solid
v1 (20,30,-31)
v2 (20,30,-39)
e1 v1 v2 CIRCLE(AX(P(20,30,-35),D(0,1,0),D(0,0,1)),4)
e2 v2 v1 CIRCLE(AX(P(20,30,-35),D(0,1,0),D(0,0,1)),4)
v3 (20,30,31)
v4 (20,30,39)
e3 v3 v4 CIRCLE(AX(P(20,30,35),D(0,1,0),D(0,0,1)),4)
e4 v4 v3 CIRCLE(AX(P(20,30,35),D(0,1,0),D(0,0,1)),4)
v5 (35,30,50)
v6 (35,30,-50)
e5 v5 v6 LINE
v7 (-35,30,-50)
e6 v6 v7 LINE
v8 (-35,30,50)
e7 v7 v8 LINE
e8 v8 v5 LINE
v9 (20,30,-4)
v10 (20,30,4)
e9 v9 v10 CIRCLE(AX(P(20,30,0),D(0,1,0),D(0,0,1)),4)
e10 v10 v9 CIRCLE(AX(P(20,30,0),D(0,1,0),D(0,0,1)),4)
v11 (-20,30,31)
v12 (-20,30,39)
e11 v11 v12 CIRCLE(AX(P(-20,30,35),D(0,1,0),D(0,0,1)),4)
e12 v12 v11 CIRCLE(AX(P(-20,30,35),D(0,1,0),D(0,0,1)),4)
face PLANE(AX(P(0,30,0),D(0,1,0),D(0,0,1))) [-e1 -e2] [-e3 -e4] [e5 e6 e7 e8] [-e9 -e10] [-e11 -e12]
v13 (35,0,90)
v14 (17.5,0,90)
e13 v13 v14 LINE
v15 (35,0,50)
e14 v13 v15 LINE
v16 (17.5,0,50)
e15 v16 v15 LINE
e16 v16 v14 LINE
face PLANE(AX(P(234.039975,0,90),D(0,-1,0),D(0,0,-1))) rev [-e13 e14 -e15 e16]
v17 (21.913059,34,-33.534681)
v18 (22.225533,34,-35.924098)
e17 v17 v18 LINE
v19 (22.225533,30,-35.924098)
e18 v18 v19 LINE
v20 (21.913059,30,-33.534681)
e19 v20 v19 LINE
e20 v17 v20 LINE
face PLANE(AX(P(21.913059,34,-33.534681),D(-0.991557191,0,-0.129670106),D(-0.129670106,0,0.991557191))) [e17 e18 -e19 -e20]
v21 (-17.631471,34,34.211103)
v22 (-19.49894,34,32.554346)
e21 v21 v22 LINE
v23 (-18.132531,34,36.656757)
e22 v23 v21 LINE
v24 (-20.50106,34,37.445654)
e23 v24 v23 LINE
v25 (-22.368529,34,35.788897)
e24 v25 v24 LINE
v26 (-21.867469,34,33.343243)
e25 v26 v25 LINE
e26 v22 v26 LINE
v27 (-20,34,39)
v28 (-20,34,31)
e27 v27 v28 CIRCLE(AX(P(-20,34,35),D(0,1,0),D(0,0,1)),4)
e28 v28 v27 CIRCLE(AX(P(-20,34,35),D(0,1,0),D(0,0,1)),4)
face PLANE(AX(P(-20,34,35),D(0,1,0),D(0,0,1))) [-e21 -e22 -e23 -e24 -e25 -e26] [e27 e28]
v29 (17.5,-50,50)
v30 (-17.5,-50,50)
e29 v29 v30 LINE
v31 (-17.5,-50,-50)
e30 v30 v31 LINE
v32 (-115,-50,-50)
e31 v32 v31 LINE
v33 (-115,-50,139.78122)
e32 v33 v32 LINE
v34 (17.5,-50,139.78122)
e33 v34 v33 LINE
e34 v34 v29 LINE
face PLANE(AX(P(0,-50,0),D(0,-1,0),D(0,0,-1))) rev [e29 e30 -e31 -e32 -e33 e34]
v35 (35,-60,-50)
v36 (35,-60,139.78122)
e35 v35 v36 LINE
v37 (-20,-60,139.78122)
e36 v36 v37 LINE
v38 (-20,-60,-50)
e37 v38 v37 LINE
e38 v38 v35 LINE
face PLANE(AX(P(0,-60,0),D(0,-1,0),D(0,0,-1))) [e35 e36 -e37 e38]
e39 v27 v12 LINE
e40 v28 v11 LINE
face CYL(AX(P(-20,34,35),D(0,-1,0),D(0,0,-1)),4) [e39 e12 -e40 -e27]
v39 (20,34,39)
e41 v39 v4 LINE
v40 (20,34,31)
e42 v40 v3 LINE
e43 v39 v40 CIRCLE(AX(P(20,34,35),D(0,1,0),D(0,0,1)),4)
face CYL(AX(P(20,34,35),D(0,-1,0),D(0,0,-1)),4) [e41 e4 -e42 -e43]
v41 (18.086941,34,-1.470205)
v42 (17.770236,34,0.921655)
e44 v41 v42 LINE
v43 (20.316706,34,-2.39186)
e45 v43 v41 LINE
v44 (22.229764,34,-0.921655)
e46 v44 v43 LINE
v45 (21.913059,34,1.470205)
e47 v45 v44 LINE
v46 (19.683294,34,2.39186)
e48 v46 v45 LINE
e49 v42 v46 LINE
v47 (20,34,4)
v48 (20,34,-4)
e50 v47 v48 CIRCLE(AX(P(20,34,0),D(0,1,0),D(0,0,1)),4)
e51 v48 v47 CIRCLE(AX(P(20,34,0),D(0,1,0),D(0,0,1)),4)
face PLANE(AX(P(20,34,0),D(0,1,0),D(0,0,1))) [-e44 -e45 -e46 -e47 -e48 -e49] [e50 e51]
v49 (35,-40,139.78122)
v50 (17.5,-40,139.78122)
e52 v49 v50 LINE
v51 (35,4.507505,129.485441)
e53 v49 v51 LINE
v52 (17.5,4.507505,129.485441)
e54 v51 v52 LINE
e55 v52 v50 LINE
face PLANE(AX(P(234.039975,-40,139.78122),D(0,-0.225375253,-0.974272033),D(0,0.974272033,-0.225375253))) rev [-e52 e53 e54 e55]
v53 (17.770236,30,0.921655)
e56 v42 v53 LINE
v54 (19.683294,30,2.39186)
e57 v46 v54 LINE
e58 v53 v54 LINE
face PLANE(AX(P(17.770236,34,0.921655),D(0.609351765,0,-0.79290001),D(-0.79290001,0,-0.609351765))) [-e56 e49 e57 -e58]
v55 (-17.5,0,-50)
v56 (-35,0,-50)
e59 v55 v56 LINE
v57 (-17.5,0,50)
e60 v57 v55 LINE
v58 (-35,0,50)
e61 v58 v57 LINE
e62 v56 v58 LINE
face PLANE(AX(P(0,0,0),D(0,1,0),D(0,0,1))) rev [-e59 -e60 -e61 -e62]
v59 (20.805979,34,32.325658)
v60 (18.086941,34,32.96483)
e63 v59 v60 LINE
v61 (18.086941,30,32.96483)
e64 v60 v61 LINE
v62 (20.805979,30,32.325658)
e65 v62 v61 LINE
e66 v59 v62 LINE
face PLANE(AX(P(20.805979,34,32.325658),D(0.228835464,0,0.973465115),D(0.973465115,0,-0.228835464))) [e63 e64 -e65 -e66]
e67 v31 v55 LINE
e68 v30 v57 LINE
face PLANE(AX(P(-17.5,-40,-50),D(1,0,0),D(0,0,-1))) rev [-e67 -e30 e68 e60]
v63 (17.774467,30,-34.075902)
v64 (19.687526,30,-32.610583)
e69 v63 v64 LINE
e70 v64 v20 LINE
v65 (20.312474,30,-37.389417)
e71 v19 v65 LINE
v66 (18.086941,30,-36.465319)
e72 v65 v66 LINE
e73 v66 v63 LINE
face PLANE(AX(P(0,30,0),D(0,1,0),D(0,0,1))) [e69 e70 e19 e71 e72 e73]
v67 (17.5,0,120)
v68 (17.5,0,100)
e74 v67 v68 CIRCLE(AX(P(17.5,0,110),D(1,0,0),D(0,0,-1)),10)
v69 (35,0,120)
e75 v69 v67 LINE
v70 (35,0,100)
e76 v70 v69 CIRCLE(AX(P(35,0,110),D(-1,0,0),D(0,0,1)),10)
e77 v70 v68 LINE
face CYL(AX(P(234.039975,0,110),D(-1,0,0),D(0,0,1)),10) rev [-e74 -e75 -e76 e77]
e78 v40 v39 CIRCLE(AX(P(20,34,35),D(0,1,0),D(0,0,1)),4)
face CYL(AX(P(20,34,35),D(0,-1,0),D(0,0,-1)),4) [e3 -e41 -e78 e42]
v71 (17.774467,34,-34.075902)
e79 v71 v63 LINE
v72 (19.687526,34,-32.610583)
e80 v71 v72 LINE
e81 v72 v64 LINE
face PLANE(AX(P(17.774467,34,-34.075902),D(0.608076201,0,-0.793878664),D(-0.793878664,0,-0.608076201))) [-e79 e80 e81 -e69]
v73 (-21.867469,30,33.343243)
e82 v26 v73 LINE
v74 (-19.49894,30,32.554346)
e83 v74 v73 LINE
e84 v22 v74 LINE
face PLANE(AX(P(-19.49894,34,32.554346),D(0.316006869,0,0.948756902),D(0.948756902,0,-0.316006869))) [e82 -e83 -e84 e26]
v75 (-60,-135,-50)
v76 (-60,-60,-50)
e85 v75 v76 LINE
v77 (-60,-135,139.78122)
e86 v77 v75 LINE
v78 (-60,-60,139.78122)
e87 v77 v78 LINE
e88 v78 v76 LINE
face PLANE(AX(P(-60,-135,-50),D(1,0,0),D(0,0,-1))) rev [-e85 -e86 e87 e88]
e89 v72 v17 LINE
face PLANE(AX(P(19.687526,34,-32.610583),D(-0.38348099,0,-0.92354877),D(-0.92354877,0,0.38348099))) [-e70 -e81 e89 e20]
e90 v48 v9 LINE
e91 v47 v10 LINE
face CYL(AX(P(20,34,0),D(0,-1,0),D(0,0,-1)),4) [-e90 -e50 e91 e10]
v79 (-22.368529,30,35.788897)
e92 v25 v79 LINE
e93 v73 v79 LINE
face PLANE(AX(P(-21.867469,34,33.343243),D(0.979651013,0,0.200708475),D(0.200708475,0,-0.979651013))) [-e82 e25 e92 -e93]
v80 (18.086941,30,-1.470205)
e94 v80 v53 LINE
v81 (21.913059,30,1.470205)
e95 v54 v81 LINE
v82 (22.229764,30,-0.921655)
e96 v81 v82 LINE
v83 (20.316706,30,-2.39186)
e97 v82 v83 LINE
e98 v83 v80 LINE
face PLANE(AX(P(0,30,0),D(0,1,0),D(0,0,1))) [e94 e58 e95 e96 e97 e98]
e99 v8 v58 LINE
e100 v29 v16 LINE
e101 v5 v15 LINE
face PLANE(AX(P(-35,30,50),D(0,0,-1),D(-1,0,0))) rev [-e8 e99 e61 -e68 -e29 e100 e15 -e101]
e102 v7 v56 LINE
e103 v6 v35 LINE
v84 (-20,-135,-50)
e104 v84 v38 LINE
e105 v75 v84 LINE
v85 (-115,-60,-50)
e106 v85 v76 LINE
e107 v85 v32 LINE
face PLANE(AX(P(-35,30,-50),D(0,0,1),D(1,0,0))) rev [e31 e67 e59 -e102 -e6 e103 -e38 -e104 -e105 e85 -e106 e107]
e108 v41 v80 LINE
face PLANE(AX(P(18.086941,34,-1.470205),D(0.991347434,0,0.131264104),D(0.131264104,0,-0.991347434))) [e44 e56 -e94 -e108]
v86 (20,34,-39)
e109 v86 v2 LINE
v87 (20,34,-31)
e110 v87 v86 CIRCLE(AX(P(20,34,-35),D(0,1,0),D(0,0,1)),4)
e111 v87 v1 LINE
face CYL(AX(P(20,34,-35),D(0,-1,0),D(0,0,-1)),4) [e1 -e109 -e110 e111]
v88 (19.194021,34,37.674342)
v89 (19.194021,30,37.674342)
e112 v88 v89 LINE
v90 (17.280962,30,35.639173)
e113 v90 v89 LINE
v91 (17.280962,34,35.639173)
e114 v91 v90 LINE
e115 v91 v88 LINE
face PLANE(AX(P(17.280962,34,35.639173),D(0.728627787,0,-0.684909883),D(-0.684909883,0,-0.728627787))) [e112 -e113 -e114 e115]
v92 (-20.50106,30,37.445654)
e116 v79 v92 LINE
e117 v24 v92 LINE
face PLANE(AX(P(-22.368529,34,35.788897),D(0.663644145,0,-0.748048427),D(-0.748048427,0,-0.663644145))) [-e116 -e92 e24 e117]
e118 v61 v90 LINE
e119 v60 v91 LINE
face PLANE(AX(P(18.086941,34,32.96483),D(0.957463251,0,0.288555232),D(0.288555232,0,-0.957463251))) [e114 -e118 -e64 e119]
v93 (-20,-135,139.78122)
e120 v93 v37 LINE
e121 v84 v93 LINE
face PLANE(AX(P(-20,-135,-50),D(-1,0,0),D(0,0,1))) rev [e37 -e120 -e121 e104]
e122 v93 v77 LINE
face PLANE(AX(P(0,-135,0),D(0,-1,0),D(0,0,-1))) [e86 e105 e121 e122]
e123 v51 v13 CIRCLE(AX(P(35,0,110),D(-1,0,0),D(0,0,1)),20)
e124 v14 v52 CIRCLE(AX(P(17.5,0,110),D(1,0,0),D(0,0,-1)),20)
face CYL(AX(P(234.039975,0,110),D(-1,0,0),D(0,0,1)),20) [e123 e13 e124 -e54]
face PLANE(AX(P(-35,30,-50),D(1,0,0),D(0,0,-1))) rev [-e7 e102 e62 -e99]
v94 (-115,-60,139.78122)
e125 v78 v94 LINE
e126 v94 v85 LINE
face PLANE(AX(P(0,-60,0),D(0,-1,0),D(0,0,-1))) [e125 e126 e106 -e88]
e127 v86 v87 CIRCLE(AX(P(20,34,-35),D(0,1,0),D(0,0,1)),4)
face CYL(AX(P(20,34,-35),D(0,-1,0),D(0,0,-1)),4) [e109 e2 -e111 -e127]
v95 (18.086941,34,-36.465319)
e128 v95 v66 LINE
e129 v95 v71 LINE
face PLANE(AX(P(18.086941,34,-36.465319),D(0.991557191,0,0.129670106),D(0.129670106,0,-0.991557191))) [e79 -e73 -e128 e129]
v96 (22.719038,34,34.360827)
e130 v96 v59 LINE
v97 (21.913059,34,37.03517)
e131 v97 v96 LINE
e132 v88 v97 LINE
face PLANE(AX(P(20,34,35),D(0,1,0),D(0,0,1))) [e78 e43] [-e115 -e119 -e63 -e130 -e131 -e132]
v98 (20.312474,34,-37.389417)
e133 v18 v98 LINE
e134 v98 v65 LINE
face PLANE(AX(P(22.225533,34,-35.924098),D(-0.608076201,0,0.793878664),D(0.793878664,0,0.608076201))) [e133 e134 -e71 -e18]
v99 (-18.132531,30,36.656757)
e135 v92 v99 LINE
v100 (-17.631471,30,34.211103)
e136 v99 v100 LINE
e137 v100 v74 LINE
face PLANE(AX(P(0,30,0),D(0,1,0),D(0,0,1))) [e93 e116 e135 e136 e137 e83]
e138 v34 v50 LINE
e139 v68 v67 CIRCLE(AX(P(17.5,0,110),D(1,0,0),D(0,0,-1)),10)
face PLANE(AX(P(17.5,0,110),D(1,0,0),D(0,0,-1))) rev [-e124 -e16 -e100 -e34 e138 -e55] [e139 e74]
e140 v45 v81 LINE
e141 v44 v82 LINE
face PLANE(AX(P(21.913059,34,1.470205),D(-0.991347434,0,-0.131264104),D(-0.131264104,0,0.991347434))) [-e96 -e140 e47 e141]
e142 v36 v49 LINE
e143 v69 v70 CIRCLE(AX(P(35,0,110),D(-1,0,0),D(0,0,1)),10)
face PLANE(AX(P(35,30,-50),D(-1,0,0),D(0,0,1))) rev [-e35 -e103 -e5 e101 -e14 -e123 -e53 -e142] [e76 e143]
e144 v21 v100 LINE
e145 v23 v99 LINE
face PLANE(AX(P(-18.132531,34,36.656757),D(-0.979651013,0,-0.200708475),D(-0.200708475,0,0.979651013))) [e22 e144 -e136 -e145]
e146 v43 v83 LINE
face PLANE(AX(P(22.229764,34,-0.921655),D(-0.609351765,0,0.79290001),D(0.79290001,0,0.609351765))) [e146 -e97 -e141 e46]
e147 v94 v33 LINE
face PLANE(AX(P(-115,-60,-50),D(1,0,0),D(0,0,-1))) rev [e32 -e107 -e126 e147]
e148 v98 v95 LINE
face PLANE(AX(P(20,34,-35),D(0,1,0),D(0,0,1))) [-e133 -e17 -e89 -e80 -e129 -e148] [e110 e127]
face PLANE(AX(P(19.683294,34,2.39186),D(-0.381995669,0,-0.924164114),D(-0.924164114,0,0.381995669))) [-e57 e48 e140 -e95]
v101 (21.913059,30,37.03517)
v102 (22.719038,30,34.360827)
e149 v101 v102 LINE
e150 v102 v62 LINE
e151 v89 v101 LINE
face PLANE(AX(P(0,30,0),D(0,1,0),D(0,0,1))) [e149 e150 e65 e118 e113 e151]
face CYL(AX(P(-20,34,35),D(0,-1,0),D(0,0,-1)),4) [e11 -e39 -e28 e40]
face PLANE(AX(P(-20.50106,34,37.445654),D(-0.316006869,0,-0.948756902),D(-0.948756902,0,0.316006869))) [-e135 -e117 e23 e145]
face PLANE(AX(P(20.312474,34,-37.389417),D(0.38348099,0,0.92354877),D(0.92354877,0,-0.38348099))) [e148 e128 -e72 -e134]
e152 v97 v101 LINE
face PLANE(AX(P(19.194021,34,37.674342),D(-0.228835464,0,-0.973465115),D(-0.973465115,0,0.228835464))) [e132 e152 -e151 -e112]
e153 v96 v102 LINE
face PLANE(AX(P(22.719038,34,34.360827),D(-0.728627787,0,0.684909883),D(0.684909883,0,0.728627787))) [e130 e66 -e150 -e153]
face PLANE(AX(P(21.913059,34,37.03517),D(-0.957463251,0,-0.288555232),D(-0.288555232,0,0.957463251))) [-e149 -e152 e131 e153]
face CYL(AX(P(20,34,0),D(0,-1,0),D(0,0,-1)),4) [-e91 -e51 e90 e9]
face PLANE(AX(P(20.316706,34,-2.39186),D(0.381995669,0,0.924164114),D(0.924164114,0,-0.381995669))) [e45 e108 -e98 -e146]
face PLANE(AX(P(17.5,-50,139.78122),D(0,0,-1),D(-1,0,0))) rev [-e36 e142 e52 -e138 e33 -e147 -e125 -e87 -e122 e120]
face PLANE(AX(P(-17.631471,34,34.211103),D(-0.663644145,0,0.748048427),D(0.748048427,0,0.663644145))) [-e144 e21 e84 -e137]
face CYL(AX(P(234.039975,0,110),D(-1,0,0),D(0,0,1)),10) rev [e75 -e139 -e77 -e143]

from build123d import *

# Parameters (mm, degrees)
SKETCH1_W           = 70
SKETCH1_H           = 100
BOSS_EXTRUDE1_DEPTH = 30
SKETCH2_R           = 4
BOSS_EXTRUDE2_DEPTH = 4
SKETCH3_W           = 35
SKETCH3_H           = 100
BOSS_EXTRUDE3_DEPTH = 40
SKETCH4_R           = 10
BOSS_EXTRUDE4_DEPTH = 17.5
BOSS_EXTRUDE5_DEPTH = 10
SKETCH6_W           = 150
SKETCH6_H           = 189.781220368
BOSS_EXTRUDE6_DEPTH = 10
SKETCH7_W           = 40
SKETCH7_H           = 189.781220368
BOSS_EXTRUDE7_DEPTH = 75


with BuildPart() as part:
    # Sketch1 → Boss-Extrude1 (new body)
    with BuildSketch(Plane(origin=(0, 0, 0), x_dir=(1, 0, 0), z_dir=(0, 1, 0))):
        Rectangle(SKETCH1_W, SKETCH1_H)
    extrude(amount=BOSS_EXTRUDE1_DEPTH)

    # Sketch2 → Boss-Extrude2 (add)
    # profile 1 of 4: a face of its own
    with BuildSketch(Plane(origin=(0, 30, 0), x_dir=(1, 0, 0), z_dir=(0, 1, 0))):
        with Locations(Location((-20, -35, 0), (0, 0, 270))):
            Circle(SKETCH2_R)
        Polygon((-18.132531053, -36.656757487), (-17.631471454, -34.211103194), (-19.498940402, -32.554345707), (-21.867468947, -33.343242513), (-22.368528546, -35.788896806), (-20.501059598, -37.445654293), align=None, mode=Mode.SUBTRACT)
    # profile 2 of 4: a face of its own
    with BuildSketch(Plane(origin=(0, 30, 0), x_dir=(1, 0, 0), z_dir=(0, 1, 0))):
        with Locations(Location((20, -35, 0), (0, 0, 270))):
            Circle(SKETCH2_R)
        Polygon((21.913058762, -37.035169602), (22.719037957, -34.360827314), (20.805979195, -32.325657712), (18.086941238, -32.964830398), (17.280962043, -35.639172686), (19.194020805, -37.674342288), align=None, mode=Mode.SUBTRACT)
    # profile 3 of 4: a face of its own
    with BuildSketch(Plane(origin=(0, 30, 0), x_dir=(1, 0, 0), z_dir=(0, 1, 0))):
        with Locations(Location((20, 0, 0), (0, 0, 270))):
            Circle(SKETCH2_R)
        Polygon((21.913058762, -1.47020522), (22.229764451, 0.921654877), (20.316705689, 2.391860097), (18.086941238, 1.47020522), (17.770235549, -0.921654877), (19.683294311, -2.391860097), align=None, mode=Mode.SUBTRACT)
    # profile 4 of 4: a face of its own
    with BuildSketch(Plane(origin=(0, 30, 0), x_dir=(1, 0, 0), z_dir=(0, 1, 0))):
        with Locations(Location((20, 35, 0), (0, 0, 270))):
            Circle(SKETCH2_R)
        Polygon((21.913058762, 33.534680981), (22.225532876, 35.924097978), (20.312474114, 37.389416996), (18.086941238, 36.465319019), (17.774467124, 34.075902022), (19.687525886, 32.610583004), align=None, mode=Mode.SUBTRACT)
    extrude(amount=BOSS_EXTRUDE2_DEPTH)

    # Sketch3 → Boss-Extrude3 (add)
    with BuildSketch(Plane.XZ):
        Rectangle(SKETCH3_W, SKETCH3_H)
    extrude(amount=BOSS_EXTRUDE3_DEPTH)

    # Sketch4 → Boss-Extrude4 (add)
    with BuildSketch(Plane(origin=(17.5, 0, 0), x_dir=(0, 0, -1), z_dir=(1, 0, 0))):
        with BuildLine():
            Line((-50, -40), (-139.781220368, -40))
            Line((-139.781220368, -40), (-129.48544067, 4.507505064))
            ThreePointArc((-129.48544067, 4.507505064), (-107.731609976, 19.87094378), (-90, 0))
            Line((-90, 0), (-50, 0))
            Line((-50, 0), (50, 0))
            Line((50, 0), (50, -40))
            Line((50, -40), (-50, -40))
        make_face()
        with Locations(Location((-110, 0, 0), (0, 0, 180))):
            Circle(SKETCH4_R, mode=Mode.SUBTRACT)
    extrude(amount=BOSS_EXTRUDE4_DEPTH)

    # Sketch5 → Boss-Extrude5 (add)
    with BuildSketch(Plane.XZ.offset(40)):
        Polygon((17.5, 139.781220368), (35, 139.781220368), (35, -50), (-17.5, -50), (-17.5, 50), (17.5, 50), align=None)
    extrude(amount=BOSS_EXTRUDE5_DEPTH)

    # Sketch6 → Boss-Extrude6 (add)
    with BuildSketch(Plane.XZ.offset(50)):
        with Locations((-40, 44.890610184)):
            Rectangle(SKETCH6_W, SKETCH6_H)
    extrude(amount=BOSS_EXTRUDE6_DEPTH)

    # Sketch7 → Boss-Extrude7 (add)
    with BuildSketch(Plane.XZ.offset(60)):
        with Locations((-40, 44.890610184)):
            Rectangle(SKETCH7_W, SKETCH7_H)
    extrude(amount=BOSS_EXTRUDE7_DEPTH)


solid = part.part
